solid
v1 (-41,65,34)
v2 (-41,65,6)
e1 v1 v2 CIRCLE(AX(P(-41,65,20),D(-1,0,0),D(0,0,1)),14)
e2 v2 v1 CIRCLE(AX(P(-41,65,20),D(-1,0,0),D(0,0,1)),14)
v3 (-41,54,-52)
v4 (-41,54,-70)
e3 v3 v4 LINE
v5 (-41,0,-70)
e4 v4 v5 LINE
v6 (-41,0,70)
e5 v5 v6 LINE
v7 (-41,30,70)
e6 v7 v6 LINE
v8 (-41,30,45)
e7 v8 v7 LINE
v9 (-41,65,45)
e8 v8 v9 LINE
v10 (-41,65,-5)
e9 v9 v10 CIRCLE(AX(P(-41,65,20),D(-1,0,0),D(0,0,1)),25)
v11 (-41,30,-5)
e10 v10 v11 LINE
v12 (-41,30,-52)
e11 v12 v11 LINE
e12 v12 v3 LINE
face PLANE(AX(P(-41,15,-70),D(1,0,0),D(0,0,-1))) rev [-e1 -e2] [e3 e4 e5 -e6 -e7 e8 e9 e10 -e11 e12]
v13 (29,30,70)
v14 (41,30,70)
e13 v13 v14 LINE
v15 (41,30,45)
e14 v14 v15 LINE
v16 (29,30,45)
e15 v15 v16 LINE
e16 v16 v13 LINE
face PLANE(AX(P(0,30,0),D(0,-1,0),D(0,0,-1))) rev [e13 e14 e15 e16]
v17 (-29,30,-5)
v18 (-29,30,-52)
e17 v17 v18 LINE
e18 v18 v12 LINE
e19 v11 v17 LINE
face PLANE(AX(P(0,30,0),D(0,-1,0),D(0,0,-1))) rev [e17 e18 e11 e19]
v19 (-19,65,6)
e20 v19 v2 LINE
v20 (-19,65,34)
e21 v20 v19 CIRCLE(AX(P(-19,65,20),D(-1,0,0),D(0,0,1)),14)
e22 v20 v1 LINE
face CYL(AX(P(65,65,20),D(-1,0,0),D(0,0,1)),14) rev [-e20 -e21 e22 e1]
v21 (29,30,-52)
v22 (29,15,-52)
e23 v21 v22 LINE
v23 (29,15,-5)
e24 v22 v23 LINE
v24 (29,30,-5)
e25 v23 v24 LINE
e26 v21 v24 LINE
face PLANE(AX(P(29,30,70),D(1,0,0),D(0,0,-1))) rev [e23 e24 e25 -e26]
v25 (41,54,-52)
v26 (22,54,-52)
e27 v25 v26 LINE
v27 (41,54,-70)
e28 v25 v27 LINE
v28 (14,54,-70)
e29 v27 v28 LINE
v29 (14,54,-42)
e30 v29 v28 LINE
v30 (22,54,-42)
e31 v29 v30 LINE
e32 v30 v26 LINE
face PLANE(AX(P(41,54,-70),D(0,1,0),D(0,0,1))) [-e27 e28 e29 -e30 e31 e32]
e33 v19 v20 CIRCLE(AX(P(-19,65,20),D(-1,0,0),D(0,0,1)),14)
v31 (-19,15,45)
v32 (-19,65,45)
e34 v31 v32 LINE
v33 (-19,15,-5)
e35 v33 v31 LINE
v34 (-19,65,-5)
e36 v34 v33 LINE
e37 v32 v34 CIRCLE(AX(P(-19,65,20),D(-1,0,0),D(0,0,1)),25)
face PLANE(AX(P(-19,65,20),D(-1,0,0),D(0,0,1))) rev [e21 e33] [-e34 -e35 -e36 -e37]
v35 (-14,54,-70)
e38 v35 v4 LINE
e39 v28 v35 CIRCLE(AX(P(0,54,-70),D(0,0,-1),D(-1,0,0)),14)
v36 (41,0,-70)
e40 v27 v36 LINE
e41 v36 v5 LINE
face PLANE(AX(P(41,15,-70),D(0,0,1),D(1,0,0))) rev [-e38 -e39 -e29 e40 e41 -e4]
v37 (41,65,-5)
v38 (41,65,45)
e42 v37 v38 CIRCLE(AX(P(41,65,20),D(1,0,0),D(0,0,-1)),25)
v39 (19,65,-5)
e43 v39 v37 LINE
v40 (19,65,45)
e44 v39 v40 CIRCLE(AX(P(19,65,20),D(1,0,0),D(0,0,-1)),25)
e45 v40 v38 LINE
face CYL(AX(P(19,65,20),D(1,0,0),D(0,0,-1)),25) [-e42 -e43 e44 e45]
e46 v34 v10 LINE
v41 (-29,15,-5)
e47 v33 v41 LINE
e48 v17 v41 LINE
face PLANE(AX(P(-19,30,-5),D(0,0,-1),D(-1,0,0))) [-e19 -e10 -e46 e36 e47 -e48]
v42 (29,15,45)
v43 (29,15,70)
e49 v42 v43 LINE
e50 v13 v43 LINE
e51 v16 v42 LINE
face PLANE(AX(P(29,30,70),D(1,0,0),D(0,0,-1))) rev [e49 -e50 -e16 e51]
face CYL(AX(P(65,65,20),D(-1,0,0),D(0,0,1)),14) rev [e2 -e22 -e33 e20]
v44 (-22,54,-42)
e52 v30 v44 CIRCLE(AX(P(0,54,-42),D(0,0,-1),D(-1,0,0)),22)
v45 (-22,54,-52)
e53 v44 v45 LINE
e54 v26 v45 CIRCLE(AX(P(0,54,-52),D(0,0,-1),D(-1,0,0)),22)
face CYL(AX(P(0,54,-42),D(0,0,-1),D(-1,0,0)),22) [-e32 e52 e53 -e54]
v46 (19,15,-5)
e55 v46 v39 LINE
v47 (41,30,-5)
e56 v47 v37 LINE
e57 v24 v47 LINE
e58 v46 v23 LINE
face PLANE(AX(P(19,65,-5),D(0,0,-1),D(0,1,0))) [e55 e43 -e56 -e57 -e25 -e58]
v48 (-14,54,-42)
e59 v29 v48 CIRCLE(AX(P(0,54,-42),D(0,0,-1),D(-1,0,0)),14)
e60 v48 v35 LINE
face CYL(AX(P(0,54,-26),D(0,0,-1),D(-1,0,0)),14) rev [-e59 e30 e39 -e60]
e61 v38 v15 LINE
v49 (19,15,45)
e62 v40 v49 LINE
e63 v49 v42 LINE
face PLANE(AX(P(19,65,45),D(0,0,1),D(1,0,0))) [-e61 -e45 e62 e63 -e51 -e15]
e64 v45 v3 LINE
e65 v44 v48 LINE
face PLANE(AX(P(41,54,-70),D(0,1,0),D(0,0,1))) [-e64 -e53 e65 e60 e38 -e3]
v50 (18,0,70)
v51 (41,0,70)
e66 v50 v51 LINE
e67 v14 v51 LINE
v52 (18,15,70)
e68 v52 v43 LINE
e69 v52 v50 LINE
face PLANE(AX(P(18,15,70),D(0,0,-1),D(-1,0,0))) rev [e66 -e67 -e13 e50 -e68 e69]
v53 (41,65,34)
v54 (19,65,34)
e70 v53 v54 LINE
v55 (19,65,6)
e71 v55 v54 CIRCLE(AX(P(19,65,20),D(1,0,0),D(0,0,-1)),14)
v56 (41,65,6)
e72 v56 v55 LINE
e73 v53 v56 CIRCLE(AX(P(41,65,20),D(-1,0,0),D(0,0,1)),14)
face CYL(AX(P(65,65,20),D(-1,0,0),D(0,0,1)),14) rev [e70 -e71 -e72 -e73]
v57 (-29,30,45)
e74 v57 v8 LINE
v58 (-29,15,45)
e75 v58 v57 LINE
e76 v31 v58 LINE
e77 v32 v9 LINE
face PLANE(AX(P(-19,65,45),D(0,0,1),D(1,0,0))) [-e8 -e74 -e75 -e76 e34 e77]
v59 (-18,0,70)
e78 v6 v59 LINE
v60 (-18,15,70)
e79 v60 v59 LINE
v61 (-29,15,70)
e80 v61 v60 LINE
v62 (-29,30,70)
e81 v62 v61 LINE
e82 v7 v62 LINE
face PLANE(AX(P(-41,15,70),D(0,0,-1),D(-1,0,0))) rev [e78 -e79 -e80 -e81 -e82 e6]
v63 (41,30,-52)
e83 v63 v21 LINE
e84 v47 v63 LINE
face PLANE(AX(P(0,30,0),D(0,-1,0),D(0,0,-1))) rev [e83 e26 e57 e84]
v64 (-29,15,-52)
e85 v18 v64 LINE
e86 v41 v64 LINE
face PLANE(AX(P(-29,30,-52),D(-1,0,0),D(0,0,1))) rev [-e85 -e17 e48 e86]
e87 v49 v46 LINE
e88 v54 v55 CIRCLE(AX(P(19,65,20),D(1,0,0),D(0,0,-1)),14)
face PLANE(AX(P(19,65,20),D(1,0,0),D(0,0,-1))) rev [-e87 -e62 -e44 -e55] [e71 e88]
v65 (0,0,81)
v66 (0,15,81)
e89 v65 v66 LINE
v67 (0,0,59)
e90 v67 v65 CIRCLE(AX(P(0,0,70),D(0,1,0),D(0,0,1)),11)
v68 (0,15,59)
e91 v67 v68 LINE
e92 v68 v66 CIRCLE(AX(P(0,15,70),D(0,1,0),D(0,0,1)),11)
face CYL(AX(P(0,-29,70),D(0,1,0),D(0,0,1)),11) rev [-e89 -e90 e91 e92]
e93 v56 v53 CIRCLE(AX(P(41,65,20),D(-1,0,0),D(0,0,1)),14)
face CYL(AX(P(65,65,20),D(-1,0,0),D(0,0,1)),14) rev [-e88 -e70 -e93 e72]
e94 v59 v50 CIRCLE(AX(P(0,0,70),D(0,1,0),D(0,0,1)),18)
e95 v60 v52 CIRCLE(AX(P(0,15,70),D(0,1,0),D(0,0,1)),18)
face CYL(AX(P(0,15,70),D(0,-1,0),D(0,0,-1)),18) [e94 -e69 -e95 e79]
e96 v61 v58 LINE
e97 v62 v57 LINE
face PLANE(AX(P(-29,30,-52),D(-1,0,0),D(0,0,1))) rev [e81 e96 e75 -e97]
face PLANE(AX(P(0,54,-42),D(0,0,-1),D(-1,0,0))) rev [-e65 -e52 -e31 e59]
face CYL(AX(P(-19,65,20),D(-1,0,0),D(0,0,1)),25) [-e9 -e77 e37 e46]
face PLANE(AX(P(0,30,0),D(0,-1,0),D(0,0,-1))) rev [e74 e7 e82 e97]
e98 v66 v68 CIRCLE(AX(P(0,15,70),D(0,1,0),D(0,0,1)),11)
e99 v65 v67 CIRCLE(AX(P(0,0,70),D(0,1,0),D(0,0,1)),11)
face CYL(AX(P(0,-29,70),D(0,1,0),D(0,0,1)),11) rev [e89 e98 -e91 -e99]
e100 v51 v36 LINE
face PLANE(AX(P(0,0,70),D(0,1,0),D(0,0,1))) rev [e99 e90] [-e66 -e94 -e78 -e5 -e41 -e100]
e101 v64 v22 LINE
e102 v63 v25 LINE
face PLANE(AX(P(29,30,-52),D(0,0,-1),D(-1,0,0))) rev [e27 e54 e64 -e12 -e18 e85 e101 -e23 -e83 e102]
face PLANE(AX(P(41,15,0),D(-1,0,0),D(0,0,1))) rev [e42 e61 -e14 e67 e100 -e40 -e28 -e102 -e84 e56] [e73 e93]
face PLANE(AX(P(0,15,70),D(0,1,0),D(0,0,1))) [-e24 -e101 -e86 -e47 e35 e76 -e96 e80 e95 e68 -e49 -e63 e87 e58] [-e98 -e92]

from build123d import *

# Parameters (mm, degrees)
BASE_PLATE_DEPTH            = 15
RAISED_WALL_DEPTH           = 15
PIVOT_LUG_DEPTH             = 22
LUG_START                   = -22
LUG_EXTENSION_DEPTH         = 22
PIVOT_BORE_SKETCH_R         = 14
PIVOT_BORE_DEPTH            = 106
BEARING_BLOCK_DEPTH         = 82
BEARING_BOSS_DEPTH          = 28
BEARING_SEAT_CUT_DEPTH      = 44
BASE_MOUNTING_HOLE_SKETCH_R = 11
BASE_MOUNTING_HOLE_DEPTH    = 44


with BuildPart() as part:
    # Base Plate Sketch → Base Plate (new body)
    with BuildSketch(Plane(origin=(0, 0, 0), x_dir=(1, 0, 0), z_dir=(0, 1, 0))):
        with BuildLine():
            Line((18, -70), (41, -70))
            Line((41, -70), (41, 0))
            Line((41, 0), (41, 70))
            Line((41, 70), (-41, 70))
            Line((-41, 70), (-41, -70))
            Line((-41, -70), (-18, -70))
            ThreePointArc((-18, -70), (0, -88), (18, -70))
        make_face()
    extrude(amount=BASE_PLATE_DEPTH)

    # Raised Wall Sketch → Raised Wall (add)
    with BuildSketch(Plane(origin=(0, 15, 0), x_dir=(1, 0, 0), z_dir=(0, 1, 0))):
        Polygon((41, -70), (29, -70), (29, 52), (-29, 52), (-29, -70), (-41, -70), (-41, 70), (41, 70), align=None)
    extrude(amount=RAISED_WALL_DEPTH)

    # Pivot Lug Sketch → Pivot Lug (add)
    with BuildSketch(Plane.ZY.offset(41)):
        with BuildLine():
            Line((45, 30), (45, 15))
            Line((45, 15), (-5, 15))
            Line((-5, 15), (-5, 30))
            Line((-5, 30), (-5, 65))
            ThreePointArc((-5, 65), (20, 90), (45, 65))
            Line((45, 65), (45, 30))
        make_face()
    extrude(amount=-PIVOT_LUG_DEPTH)

    # Lug Extension Sketch → Lug Extension (add)
    with BuildSketch(Plane(origin=(41, 0, 0), x_dir=(0, 0, -1), z_dir=(1, 0, 0)).offset(LUG_START)):
        with BuildLine():
            Line((5, 15), (-20, 15))
            Line((-20, 15), (-45, 15))
            Line((-45, 15), (-45, 65))
            ThreePointArc((-45, 65), (-20, 90), (5, 65))
            Line((5, 65), (5, 15))
        make_face()
    extrude(amount=LUG_EXTENSION_DEPTH)

    # Pivot Bore Sketch → Pivot Bore (cut)
    with BuildSketch(Plane.ZY.offset(41)):
        with Locations((20, 65)):
            Circle(PIVOT_BORE_SKETCH_R)
    extrude(amount=-PIVOT_BORE_DEPTH, mode=Mode.SUBTRACT)

    # Bearing Block Sketch → Bearing Block (add)
    with BuildSketch(Plane.ZY.offset(41)):
        Polygon((-70, 0), (-70, 54), (-52, 54), (-52, 30), (-52, 0), align=None)
    extrude(amount=-BEARING_BLOCK_DEPTH)

    # Bearing Boss Sketch → Bearing Boss (add)
    with BuildSketch(Plane(origin=(0, 0, -70), x_dir=(-1, 0, 0), z_dir=(0, 0, -1))):
        with BuildLine():
            Line((-22, 54), (22, 54))
            ThreePointArc((22, 54), (0, 32), (-22, 54))
        make_face()
    extrude(amount=-BEARING_BOSS_DEPTH)

    # Bearing Seat Sketch → Bearing Seat Cut (cut)
    with BuildSketch(Plane(origin=(0, 0, -70), x_dir=(-1, 0, 0), z_dir=(0, 0, -1))):
        with BuildLine():
            Line((-14, 54), (14, 54))
            ThreePointArc((14, 54), (0, 40), (-14, 54))
        make_face()
    extrude(amount=-BEARING_SEAT_CUT_DEPTH, mode=Mode.SUBTRACT)

    # Base Mounting Hole Sketch → Base Mounting Hole (cut)
    with BuildSketch(Plane(origin=(0, 15, 0), x_dir=(1, 0, 0), z_dir=(0, 1, 0))):
        with Locations(Location((0, -70, 0), (0, 0, 270))):
            Circle(BASE_MOUNTING_HOLE_SKETCH_R)
    extrude(amount=-BASE_MOUNTING_HOLE_DEPTH, mode=Mode.SUBTRACT)


solid = part.part
